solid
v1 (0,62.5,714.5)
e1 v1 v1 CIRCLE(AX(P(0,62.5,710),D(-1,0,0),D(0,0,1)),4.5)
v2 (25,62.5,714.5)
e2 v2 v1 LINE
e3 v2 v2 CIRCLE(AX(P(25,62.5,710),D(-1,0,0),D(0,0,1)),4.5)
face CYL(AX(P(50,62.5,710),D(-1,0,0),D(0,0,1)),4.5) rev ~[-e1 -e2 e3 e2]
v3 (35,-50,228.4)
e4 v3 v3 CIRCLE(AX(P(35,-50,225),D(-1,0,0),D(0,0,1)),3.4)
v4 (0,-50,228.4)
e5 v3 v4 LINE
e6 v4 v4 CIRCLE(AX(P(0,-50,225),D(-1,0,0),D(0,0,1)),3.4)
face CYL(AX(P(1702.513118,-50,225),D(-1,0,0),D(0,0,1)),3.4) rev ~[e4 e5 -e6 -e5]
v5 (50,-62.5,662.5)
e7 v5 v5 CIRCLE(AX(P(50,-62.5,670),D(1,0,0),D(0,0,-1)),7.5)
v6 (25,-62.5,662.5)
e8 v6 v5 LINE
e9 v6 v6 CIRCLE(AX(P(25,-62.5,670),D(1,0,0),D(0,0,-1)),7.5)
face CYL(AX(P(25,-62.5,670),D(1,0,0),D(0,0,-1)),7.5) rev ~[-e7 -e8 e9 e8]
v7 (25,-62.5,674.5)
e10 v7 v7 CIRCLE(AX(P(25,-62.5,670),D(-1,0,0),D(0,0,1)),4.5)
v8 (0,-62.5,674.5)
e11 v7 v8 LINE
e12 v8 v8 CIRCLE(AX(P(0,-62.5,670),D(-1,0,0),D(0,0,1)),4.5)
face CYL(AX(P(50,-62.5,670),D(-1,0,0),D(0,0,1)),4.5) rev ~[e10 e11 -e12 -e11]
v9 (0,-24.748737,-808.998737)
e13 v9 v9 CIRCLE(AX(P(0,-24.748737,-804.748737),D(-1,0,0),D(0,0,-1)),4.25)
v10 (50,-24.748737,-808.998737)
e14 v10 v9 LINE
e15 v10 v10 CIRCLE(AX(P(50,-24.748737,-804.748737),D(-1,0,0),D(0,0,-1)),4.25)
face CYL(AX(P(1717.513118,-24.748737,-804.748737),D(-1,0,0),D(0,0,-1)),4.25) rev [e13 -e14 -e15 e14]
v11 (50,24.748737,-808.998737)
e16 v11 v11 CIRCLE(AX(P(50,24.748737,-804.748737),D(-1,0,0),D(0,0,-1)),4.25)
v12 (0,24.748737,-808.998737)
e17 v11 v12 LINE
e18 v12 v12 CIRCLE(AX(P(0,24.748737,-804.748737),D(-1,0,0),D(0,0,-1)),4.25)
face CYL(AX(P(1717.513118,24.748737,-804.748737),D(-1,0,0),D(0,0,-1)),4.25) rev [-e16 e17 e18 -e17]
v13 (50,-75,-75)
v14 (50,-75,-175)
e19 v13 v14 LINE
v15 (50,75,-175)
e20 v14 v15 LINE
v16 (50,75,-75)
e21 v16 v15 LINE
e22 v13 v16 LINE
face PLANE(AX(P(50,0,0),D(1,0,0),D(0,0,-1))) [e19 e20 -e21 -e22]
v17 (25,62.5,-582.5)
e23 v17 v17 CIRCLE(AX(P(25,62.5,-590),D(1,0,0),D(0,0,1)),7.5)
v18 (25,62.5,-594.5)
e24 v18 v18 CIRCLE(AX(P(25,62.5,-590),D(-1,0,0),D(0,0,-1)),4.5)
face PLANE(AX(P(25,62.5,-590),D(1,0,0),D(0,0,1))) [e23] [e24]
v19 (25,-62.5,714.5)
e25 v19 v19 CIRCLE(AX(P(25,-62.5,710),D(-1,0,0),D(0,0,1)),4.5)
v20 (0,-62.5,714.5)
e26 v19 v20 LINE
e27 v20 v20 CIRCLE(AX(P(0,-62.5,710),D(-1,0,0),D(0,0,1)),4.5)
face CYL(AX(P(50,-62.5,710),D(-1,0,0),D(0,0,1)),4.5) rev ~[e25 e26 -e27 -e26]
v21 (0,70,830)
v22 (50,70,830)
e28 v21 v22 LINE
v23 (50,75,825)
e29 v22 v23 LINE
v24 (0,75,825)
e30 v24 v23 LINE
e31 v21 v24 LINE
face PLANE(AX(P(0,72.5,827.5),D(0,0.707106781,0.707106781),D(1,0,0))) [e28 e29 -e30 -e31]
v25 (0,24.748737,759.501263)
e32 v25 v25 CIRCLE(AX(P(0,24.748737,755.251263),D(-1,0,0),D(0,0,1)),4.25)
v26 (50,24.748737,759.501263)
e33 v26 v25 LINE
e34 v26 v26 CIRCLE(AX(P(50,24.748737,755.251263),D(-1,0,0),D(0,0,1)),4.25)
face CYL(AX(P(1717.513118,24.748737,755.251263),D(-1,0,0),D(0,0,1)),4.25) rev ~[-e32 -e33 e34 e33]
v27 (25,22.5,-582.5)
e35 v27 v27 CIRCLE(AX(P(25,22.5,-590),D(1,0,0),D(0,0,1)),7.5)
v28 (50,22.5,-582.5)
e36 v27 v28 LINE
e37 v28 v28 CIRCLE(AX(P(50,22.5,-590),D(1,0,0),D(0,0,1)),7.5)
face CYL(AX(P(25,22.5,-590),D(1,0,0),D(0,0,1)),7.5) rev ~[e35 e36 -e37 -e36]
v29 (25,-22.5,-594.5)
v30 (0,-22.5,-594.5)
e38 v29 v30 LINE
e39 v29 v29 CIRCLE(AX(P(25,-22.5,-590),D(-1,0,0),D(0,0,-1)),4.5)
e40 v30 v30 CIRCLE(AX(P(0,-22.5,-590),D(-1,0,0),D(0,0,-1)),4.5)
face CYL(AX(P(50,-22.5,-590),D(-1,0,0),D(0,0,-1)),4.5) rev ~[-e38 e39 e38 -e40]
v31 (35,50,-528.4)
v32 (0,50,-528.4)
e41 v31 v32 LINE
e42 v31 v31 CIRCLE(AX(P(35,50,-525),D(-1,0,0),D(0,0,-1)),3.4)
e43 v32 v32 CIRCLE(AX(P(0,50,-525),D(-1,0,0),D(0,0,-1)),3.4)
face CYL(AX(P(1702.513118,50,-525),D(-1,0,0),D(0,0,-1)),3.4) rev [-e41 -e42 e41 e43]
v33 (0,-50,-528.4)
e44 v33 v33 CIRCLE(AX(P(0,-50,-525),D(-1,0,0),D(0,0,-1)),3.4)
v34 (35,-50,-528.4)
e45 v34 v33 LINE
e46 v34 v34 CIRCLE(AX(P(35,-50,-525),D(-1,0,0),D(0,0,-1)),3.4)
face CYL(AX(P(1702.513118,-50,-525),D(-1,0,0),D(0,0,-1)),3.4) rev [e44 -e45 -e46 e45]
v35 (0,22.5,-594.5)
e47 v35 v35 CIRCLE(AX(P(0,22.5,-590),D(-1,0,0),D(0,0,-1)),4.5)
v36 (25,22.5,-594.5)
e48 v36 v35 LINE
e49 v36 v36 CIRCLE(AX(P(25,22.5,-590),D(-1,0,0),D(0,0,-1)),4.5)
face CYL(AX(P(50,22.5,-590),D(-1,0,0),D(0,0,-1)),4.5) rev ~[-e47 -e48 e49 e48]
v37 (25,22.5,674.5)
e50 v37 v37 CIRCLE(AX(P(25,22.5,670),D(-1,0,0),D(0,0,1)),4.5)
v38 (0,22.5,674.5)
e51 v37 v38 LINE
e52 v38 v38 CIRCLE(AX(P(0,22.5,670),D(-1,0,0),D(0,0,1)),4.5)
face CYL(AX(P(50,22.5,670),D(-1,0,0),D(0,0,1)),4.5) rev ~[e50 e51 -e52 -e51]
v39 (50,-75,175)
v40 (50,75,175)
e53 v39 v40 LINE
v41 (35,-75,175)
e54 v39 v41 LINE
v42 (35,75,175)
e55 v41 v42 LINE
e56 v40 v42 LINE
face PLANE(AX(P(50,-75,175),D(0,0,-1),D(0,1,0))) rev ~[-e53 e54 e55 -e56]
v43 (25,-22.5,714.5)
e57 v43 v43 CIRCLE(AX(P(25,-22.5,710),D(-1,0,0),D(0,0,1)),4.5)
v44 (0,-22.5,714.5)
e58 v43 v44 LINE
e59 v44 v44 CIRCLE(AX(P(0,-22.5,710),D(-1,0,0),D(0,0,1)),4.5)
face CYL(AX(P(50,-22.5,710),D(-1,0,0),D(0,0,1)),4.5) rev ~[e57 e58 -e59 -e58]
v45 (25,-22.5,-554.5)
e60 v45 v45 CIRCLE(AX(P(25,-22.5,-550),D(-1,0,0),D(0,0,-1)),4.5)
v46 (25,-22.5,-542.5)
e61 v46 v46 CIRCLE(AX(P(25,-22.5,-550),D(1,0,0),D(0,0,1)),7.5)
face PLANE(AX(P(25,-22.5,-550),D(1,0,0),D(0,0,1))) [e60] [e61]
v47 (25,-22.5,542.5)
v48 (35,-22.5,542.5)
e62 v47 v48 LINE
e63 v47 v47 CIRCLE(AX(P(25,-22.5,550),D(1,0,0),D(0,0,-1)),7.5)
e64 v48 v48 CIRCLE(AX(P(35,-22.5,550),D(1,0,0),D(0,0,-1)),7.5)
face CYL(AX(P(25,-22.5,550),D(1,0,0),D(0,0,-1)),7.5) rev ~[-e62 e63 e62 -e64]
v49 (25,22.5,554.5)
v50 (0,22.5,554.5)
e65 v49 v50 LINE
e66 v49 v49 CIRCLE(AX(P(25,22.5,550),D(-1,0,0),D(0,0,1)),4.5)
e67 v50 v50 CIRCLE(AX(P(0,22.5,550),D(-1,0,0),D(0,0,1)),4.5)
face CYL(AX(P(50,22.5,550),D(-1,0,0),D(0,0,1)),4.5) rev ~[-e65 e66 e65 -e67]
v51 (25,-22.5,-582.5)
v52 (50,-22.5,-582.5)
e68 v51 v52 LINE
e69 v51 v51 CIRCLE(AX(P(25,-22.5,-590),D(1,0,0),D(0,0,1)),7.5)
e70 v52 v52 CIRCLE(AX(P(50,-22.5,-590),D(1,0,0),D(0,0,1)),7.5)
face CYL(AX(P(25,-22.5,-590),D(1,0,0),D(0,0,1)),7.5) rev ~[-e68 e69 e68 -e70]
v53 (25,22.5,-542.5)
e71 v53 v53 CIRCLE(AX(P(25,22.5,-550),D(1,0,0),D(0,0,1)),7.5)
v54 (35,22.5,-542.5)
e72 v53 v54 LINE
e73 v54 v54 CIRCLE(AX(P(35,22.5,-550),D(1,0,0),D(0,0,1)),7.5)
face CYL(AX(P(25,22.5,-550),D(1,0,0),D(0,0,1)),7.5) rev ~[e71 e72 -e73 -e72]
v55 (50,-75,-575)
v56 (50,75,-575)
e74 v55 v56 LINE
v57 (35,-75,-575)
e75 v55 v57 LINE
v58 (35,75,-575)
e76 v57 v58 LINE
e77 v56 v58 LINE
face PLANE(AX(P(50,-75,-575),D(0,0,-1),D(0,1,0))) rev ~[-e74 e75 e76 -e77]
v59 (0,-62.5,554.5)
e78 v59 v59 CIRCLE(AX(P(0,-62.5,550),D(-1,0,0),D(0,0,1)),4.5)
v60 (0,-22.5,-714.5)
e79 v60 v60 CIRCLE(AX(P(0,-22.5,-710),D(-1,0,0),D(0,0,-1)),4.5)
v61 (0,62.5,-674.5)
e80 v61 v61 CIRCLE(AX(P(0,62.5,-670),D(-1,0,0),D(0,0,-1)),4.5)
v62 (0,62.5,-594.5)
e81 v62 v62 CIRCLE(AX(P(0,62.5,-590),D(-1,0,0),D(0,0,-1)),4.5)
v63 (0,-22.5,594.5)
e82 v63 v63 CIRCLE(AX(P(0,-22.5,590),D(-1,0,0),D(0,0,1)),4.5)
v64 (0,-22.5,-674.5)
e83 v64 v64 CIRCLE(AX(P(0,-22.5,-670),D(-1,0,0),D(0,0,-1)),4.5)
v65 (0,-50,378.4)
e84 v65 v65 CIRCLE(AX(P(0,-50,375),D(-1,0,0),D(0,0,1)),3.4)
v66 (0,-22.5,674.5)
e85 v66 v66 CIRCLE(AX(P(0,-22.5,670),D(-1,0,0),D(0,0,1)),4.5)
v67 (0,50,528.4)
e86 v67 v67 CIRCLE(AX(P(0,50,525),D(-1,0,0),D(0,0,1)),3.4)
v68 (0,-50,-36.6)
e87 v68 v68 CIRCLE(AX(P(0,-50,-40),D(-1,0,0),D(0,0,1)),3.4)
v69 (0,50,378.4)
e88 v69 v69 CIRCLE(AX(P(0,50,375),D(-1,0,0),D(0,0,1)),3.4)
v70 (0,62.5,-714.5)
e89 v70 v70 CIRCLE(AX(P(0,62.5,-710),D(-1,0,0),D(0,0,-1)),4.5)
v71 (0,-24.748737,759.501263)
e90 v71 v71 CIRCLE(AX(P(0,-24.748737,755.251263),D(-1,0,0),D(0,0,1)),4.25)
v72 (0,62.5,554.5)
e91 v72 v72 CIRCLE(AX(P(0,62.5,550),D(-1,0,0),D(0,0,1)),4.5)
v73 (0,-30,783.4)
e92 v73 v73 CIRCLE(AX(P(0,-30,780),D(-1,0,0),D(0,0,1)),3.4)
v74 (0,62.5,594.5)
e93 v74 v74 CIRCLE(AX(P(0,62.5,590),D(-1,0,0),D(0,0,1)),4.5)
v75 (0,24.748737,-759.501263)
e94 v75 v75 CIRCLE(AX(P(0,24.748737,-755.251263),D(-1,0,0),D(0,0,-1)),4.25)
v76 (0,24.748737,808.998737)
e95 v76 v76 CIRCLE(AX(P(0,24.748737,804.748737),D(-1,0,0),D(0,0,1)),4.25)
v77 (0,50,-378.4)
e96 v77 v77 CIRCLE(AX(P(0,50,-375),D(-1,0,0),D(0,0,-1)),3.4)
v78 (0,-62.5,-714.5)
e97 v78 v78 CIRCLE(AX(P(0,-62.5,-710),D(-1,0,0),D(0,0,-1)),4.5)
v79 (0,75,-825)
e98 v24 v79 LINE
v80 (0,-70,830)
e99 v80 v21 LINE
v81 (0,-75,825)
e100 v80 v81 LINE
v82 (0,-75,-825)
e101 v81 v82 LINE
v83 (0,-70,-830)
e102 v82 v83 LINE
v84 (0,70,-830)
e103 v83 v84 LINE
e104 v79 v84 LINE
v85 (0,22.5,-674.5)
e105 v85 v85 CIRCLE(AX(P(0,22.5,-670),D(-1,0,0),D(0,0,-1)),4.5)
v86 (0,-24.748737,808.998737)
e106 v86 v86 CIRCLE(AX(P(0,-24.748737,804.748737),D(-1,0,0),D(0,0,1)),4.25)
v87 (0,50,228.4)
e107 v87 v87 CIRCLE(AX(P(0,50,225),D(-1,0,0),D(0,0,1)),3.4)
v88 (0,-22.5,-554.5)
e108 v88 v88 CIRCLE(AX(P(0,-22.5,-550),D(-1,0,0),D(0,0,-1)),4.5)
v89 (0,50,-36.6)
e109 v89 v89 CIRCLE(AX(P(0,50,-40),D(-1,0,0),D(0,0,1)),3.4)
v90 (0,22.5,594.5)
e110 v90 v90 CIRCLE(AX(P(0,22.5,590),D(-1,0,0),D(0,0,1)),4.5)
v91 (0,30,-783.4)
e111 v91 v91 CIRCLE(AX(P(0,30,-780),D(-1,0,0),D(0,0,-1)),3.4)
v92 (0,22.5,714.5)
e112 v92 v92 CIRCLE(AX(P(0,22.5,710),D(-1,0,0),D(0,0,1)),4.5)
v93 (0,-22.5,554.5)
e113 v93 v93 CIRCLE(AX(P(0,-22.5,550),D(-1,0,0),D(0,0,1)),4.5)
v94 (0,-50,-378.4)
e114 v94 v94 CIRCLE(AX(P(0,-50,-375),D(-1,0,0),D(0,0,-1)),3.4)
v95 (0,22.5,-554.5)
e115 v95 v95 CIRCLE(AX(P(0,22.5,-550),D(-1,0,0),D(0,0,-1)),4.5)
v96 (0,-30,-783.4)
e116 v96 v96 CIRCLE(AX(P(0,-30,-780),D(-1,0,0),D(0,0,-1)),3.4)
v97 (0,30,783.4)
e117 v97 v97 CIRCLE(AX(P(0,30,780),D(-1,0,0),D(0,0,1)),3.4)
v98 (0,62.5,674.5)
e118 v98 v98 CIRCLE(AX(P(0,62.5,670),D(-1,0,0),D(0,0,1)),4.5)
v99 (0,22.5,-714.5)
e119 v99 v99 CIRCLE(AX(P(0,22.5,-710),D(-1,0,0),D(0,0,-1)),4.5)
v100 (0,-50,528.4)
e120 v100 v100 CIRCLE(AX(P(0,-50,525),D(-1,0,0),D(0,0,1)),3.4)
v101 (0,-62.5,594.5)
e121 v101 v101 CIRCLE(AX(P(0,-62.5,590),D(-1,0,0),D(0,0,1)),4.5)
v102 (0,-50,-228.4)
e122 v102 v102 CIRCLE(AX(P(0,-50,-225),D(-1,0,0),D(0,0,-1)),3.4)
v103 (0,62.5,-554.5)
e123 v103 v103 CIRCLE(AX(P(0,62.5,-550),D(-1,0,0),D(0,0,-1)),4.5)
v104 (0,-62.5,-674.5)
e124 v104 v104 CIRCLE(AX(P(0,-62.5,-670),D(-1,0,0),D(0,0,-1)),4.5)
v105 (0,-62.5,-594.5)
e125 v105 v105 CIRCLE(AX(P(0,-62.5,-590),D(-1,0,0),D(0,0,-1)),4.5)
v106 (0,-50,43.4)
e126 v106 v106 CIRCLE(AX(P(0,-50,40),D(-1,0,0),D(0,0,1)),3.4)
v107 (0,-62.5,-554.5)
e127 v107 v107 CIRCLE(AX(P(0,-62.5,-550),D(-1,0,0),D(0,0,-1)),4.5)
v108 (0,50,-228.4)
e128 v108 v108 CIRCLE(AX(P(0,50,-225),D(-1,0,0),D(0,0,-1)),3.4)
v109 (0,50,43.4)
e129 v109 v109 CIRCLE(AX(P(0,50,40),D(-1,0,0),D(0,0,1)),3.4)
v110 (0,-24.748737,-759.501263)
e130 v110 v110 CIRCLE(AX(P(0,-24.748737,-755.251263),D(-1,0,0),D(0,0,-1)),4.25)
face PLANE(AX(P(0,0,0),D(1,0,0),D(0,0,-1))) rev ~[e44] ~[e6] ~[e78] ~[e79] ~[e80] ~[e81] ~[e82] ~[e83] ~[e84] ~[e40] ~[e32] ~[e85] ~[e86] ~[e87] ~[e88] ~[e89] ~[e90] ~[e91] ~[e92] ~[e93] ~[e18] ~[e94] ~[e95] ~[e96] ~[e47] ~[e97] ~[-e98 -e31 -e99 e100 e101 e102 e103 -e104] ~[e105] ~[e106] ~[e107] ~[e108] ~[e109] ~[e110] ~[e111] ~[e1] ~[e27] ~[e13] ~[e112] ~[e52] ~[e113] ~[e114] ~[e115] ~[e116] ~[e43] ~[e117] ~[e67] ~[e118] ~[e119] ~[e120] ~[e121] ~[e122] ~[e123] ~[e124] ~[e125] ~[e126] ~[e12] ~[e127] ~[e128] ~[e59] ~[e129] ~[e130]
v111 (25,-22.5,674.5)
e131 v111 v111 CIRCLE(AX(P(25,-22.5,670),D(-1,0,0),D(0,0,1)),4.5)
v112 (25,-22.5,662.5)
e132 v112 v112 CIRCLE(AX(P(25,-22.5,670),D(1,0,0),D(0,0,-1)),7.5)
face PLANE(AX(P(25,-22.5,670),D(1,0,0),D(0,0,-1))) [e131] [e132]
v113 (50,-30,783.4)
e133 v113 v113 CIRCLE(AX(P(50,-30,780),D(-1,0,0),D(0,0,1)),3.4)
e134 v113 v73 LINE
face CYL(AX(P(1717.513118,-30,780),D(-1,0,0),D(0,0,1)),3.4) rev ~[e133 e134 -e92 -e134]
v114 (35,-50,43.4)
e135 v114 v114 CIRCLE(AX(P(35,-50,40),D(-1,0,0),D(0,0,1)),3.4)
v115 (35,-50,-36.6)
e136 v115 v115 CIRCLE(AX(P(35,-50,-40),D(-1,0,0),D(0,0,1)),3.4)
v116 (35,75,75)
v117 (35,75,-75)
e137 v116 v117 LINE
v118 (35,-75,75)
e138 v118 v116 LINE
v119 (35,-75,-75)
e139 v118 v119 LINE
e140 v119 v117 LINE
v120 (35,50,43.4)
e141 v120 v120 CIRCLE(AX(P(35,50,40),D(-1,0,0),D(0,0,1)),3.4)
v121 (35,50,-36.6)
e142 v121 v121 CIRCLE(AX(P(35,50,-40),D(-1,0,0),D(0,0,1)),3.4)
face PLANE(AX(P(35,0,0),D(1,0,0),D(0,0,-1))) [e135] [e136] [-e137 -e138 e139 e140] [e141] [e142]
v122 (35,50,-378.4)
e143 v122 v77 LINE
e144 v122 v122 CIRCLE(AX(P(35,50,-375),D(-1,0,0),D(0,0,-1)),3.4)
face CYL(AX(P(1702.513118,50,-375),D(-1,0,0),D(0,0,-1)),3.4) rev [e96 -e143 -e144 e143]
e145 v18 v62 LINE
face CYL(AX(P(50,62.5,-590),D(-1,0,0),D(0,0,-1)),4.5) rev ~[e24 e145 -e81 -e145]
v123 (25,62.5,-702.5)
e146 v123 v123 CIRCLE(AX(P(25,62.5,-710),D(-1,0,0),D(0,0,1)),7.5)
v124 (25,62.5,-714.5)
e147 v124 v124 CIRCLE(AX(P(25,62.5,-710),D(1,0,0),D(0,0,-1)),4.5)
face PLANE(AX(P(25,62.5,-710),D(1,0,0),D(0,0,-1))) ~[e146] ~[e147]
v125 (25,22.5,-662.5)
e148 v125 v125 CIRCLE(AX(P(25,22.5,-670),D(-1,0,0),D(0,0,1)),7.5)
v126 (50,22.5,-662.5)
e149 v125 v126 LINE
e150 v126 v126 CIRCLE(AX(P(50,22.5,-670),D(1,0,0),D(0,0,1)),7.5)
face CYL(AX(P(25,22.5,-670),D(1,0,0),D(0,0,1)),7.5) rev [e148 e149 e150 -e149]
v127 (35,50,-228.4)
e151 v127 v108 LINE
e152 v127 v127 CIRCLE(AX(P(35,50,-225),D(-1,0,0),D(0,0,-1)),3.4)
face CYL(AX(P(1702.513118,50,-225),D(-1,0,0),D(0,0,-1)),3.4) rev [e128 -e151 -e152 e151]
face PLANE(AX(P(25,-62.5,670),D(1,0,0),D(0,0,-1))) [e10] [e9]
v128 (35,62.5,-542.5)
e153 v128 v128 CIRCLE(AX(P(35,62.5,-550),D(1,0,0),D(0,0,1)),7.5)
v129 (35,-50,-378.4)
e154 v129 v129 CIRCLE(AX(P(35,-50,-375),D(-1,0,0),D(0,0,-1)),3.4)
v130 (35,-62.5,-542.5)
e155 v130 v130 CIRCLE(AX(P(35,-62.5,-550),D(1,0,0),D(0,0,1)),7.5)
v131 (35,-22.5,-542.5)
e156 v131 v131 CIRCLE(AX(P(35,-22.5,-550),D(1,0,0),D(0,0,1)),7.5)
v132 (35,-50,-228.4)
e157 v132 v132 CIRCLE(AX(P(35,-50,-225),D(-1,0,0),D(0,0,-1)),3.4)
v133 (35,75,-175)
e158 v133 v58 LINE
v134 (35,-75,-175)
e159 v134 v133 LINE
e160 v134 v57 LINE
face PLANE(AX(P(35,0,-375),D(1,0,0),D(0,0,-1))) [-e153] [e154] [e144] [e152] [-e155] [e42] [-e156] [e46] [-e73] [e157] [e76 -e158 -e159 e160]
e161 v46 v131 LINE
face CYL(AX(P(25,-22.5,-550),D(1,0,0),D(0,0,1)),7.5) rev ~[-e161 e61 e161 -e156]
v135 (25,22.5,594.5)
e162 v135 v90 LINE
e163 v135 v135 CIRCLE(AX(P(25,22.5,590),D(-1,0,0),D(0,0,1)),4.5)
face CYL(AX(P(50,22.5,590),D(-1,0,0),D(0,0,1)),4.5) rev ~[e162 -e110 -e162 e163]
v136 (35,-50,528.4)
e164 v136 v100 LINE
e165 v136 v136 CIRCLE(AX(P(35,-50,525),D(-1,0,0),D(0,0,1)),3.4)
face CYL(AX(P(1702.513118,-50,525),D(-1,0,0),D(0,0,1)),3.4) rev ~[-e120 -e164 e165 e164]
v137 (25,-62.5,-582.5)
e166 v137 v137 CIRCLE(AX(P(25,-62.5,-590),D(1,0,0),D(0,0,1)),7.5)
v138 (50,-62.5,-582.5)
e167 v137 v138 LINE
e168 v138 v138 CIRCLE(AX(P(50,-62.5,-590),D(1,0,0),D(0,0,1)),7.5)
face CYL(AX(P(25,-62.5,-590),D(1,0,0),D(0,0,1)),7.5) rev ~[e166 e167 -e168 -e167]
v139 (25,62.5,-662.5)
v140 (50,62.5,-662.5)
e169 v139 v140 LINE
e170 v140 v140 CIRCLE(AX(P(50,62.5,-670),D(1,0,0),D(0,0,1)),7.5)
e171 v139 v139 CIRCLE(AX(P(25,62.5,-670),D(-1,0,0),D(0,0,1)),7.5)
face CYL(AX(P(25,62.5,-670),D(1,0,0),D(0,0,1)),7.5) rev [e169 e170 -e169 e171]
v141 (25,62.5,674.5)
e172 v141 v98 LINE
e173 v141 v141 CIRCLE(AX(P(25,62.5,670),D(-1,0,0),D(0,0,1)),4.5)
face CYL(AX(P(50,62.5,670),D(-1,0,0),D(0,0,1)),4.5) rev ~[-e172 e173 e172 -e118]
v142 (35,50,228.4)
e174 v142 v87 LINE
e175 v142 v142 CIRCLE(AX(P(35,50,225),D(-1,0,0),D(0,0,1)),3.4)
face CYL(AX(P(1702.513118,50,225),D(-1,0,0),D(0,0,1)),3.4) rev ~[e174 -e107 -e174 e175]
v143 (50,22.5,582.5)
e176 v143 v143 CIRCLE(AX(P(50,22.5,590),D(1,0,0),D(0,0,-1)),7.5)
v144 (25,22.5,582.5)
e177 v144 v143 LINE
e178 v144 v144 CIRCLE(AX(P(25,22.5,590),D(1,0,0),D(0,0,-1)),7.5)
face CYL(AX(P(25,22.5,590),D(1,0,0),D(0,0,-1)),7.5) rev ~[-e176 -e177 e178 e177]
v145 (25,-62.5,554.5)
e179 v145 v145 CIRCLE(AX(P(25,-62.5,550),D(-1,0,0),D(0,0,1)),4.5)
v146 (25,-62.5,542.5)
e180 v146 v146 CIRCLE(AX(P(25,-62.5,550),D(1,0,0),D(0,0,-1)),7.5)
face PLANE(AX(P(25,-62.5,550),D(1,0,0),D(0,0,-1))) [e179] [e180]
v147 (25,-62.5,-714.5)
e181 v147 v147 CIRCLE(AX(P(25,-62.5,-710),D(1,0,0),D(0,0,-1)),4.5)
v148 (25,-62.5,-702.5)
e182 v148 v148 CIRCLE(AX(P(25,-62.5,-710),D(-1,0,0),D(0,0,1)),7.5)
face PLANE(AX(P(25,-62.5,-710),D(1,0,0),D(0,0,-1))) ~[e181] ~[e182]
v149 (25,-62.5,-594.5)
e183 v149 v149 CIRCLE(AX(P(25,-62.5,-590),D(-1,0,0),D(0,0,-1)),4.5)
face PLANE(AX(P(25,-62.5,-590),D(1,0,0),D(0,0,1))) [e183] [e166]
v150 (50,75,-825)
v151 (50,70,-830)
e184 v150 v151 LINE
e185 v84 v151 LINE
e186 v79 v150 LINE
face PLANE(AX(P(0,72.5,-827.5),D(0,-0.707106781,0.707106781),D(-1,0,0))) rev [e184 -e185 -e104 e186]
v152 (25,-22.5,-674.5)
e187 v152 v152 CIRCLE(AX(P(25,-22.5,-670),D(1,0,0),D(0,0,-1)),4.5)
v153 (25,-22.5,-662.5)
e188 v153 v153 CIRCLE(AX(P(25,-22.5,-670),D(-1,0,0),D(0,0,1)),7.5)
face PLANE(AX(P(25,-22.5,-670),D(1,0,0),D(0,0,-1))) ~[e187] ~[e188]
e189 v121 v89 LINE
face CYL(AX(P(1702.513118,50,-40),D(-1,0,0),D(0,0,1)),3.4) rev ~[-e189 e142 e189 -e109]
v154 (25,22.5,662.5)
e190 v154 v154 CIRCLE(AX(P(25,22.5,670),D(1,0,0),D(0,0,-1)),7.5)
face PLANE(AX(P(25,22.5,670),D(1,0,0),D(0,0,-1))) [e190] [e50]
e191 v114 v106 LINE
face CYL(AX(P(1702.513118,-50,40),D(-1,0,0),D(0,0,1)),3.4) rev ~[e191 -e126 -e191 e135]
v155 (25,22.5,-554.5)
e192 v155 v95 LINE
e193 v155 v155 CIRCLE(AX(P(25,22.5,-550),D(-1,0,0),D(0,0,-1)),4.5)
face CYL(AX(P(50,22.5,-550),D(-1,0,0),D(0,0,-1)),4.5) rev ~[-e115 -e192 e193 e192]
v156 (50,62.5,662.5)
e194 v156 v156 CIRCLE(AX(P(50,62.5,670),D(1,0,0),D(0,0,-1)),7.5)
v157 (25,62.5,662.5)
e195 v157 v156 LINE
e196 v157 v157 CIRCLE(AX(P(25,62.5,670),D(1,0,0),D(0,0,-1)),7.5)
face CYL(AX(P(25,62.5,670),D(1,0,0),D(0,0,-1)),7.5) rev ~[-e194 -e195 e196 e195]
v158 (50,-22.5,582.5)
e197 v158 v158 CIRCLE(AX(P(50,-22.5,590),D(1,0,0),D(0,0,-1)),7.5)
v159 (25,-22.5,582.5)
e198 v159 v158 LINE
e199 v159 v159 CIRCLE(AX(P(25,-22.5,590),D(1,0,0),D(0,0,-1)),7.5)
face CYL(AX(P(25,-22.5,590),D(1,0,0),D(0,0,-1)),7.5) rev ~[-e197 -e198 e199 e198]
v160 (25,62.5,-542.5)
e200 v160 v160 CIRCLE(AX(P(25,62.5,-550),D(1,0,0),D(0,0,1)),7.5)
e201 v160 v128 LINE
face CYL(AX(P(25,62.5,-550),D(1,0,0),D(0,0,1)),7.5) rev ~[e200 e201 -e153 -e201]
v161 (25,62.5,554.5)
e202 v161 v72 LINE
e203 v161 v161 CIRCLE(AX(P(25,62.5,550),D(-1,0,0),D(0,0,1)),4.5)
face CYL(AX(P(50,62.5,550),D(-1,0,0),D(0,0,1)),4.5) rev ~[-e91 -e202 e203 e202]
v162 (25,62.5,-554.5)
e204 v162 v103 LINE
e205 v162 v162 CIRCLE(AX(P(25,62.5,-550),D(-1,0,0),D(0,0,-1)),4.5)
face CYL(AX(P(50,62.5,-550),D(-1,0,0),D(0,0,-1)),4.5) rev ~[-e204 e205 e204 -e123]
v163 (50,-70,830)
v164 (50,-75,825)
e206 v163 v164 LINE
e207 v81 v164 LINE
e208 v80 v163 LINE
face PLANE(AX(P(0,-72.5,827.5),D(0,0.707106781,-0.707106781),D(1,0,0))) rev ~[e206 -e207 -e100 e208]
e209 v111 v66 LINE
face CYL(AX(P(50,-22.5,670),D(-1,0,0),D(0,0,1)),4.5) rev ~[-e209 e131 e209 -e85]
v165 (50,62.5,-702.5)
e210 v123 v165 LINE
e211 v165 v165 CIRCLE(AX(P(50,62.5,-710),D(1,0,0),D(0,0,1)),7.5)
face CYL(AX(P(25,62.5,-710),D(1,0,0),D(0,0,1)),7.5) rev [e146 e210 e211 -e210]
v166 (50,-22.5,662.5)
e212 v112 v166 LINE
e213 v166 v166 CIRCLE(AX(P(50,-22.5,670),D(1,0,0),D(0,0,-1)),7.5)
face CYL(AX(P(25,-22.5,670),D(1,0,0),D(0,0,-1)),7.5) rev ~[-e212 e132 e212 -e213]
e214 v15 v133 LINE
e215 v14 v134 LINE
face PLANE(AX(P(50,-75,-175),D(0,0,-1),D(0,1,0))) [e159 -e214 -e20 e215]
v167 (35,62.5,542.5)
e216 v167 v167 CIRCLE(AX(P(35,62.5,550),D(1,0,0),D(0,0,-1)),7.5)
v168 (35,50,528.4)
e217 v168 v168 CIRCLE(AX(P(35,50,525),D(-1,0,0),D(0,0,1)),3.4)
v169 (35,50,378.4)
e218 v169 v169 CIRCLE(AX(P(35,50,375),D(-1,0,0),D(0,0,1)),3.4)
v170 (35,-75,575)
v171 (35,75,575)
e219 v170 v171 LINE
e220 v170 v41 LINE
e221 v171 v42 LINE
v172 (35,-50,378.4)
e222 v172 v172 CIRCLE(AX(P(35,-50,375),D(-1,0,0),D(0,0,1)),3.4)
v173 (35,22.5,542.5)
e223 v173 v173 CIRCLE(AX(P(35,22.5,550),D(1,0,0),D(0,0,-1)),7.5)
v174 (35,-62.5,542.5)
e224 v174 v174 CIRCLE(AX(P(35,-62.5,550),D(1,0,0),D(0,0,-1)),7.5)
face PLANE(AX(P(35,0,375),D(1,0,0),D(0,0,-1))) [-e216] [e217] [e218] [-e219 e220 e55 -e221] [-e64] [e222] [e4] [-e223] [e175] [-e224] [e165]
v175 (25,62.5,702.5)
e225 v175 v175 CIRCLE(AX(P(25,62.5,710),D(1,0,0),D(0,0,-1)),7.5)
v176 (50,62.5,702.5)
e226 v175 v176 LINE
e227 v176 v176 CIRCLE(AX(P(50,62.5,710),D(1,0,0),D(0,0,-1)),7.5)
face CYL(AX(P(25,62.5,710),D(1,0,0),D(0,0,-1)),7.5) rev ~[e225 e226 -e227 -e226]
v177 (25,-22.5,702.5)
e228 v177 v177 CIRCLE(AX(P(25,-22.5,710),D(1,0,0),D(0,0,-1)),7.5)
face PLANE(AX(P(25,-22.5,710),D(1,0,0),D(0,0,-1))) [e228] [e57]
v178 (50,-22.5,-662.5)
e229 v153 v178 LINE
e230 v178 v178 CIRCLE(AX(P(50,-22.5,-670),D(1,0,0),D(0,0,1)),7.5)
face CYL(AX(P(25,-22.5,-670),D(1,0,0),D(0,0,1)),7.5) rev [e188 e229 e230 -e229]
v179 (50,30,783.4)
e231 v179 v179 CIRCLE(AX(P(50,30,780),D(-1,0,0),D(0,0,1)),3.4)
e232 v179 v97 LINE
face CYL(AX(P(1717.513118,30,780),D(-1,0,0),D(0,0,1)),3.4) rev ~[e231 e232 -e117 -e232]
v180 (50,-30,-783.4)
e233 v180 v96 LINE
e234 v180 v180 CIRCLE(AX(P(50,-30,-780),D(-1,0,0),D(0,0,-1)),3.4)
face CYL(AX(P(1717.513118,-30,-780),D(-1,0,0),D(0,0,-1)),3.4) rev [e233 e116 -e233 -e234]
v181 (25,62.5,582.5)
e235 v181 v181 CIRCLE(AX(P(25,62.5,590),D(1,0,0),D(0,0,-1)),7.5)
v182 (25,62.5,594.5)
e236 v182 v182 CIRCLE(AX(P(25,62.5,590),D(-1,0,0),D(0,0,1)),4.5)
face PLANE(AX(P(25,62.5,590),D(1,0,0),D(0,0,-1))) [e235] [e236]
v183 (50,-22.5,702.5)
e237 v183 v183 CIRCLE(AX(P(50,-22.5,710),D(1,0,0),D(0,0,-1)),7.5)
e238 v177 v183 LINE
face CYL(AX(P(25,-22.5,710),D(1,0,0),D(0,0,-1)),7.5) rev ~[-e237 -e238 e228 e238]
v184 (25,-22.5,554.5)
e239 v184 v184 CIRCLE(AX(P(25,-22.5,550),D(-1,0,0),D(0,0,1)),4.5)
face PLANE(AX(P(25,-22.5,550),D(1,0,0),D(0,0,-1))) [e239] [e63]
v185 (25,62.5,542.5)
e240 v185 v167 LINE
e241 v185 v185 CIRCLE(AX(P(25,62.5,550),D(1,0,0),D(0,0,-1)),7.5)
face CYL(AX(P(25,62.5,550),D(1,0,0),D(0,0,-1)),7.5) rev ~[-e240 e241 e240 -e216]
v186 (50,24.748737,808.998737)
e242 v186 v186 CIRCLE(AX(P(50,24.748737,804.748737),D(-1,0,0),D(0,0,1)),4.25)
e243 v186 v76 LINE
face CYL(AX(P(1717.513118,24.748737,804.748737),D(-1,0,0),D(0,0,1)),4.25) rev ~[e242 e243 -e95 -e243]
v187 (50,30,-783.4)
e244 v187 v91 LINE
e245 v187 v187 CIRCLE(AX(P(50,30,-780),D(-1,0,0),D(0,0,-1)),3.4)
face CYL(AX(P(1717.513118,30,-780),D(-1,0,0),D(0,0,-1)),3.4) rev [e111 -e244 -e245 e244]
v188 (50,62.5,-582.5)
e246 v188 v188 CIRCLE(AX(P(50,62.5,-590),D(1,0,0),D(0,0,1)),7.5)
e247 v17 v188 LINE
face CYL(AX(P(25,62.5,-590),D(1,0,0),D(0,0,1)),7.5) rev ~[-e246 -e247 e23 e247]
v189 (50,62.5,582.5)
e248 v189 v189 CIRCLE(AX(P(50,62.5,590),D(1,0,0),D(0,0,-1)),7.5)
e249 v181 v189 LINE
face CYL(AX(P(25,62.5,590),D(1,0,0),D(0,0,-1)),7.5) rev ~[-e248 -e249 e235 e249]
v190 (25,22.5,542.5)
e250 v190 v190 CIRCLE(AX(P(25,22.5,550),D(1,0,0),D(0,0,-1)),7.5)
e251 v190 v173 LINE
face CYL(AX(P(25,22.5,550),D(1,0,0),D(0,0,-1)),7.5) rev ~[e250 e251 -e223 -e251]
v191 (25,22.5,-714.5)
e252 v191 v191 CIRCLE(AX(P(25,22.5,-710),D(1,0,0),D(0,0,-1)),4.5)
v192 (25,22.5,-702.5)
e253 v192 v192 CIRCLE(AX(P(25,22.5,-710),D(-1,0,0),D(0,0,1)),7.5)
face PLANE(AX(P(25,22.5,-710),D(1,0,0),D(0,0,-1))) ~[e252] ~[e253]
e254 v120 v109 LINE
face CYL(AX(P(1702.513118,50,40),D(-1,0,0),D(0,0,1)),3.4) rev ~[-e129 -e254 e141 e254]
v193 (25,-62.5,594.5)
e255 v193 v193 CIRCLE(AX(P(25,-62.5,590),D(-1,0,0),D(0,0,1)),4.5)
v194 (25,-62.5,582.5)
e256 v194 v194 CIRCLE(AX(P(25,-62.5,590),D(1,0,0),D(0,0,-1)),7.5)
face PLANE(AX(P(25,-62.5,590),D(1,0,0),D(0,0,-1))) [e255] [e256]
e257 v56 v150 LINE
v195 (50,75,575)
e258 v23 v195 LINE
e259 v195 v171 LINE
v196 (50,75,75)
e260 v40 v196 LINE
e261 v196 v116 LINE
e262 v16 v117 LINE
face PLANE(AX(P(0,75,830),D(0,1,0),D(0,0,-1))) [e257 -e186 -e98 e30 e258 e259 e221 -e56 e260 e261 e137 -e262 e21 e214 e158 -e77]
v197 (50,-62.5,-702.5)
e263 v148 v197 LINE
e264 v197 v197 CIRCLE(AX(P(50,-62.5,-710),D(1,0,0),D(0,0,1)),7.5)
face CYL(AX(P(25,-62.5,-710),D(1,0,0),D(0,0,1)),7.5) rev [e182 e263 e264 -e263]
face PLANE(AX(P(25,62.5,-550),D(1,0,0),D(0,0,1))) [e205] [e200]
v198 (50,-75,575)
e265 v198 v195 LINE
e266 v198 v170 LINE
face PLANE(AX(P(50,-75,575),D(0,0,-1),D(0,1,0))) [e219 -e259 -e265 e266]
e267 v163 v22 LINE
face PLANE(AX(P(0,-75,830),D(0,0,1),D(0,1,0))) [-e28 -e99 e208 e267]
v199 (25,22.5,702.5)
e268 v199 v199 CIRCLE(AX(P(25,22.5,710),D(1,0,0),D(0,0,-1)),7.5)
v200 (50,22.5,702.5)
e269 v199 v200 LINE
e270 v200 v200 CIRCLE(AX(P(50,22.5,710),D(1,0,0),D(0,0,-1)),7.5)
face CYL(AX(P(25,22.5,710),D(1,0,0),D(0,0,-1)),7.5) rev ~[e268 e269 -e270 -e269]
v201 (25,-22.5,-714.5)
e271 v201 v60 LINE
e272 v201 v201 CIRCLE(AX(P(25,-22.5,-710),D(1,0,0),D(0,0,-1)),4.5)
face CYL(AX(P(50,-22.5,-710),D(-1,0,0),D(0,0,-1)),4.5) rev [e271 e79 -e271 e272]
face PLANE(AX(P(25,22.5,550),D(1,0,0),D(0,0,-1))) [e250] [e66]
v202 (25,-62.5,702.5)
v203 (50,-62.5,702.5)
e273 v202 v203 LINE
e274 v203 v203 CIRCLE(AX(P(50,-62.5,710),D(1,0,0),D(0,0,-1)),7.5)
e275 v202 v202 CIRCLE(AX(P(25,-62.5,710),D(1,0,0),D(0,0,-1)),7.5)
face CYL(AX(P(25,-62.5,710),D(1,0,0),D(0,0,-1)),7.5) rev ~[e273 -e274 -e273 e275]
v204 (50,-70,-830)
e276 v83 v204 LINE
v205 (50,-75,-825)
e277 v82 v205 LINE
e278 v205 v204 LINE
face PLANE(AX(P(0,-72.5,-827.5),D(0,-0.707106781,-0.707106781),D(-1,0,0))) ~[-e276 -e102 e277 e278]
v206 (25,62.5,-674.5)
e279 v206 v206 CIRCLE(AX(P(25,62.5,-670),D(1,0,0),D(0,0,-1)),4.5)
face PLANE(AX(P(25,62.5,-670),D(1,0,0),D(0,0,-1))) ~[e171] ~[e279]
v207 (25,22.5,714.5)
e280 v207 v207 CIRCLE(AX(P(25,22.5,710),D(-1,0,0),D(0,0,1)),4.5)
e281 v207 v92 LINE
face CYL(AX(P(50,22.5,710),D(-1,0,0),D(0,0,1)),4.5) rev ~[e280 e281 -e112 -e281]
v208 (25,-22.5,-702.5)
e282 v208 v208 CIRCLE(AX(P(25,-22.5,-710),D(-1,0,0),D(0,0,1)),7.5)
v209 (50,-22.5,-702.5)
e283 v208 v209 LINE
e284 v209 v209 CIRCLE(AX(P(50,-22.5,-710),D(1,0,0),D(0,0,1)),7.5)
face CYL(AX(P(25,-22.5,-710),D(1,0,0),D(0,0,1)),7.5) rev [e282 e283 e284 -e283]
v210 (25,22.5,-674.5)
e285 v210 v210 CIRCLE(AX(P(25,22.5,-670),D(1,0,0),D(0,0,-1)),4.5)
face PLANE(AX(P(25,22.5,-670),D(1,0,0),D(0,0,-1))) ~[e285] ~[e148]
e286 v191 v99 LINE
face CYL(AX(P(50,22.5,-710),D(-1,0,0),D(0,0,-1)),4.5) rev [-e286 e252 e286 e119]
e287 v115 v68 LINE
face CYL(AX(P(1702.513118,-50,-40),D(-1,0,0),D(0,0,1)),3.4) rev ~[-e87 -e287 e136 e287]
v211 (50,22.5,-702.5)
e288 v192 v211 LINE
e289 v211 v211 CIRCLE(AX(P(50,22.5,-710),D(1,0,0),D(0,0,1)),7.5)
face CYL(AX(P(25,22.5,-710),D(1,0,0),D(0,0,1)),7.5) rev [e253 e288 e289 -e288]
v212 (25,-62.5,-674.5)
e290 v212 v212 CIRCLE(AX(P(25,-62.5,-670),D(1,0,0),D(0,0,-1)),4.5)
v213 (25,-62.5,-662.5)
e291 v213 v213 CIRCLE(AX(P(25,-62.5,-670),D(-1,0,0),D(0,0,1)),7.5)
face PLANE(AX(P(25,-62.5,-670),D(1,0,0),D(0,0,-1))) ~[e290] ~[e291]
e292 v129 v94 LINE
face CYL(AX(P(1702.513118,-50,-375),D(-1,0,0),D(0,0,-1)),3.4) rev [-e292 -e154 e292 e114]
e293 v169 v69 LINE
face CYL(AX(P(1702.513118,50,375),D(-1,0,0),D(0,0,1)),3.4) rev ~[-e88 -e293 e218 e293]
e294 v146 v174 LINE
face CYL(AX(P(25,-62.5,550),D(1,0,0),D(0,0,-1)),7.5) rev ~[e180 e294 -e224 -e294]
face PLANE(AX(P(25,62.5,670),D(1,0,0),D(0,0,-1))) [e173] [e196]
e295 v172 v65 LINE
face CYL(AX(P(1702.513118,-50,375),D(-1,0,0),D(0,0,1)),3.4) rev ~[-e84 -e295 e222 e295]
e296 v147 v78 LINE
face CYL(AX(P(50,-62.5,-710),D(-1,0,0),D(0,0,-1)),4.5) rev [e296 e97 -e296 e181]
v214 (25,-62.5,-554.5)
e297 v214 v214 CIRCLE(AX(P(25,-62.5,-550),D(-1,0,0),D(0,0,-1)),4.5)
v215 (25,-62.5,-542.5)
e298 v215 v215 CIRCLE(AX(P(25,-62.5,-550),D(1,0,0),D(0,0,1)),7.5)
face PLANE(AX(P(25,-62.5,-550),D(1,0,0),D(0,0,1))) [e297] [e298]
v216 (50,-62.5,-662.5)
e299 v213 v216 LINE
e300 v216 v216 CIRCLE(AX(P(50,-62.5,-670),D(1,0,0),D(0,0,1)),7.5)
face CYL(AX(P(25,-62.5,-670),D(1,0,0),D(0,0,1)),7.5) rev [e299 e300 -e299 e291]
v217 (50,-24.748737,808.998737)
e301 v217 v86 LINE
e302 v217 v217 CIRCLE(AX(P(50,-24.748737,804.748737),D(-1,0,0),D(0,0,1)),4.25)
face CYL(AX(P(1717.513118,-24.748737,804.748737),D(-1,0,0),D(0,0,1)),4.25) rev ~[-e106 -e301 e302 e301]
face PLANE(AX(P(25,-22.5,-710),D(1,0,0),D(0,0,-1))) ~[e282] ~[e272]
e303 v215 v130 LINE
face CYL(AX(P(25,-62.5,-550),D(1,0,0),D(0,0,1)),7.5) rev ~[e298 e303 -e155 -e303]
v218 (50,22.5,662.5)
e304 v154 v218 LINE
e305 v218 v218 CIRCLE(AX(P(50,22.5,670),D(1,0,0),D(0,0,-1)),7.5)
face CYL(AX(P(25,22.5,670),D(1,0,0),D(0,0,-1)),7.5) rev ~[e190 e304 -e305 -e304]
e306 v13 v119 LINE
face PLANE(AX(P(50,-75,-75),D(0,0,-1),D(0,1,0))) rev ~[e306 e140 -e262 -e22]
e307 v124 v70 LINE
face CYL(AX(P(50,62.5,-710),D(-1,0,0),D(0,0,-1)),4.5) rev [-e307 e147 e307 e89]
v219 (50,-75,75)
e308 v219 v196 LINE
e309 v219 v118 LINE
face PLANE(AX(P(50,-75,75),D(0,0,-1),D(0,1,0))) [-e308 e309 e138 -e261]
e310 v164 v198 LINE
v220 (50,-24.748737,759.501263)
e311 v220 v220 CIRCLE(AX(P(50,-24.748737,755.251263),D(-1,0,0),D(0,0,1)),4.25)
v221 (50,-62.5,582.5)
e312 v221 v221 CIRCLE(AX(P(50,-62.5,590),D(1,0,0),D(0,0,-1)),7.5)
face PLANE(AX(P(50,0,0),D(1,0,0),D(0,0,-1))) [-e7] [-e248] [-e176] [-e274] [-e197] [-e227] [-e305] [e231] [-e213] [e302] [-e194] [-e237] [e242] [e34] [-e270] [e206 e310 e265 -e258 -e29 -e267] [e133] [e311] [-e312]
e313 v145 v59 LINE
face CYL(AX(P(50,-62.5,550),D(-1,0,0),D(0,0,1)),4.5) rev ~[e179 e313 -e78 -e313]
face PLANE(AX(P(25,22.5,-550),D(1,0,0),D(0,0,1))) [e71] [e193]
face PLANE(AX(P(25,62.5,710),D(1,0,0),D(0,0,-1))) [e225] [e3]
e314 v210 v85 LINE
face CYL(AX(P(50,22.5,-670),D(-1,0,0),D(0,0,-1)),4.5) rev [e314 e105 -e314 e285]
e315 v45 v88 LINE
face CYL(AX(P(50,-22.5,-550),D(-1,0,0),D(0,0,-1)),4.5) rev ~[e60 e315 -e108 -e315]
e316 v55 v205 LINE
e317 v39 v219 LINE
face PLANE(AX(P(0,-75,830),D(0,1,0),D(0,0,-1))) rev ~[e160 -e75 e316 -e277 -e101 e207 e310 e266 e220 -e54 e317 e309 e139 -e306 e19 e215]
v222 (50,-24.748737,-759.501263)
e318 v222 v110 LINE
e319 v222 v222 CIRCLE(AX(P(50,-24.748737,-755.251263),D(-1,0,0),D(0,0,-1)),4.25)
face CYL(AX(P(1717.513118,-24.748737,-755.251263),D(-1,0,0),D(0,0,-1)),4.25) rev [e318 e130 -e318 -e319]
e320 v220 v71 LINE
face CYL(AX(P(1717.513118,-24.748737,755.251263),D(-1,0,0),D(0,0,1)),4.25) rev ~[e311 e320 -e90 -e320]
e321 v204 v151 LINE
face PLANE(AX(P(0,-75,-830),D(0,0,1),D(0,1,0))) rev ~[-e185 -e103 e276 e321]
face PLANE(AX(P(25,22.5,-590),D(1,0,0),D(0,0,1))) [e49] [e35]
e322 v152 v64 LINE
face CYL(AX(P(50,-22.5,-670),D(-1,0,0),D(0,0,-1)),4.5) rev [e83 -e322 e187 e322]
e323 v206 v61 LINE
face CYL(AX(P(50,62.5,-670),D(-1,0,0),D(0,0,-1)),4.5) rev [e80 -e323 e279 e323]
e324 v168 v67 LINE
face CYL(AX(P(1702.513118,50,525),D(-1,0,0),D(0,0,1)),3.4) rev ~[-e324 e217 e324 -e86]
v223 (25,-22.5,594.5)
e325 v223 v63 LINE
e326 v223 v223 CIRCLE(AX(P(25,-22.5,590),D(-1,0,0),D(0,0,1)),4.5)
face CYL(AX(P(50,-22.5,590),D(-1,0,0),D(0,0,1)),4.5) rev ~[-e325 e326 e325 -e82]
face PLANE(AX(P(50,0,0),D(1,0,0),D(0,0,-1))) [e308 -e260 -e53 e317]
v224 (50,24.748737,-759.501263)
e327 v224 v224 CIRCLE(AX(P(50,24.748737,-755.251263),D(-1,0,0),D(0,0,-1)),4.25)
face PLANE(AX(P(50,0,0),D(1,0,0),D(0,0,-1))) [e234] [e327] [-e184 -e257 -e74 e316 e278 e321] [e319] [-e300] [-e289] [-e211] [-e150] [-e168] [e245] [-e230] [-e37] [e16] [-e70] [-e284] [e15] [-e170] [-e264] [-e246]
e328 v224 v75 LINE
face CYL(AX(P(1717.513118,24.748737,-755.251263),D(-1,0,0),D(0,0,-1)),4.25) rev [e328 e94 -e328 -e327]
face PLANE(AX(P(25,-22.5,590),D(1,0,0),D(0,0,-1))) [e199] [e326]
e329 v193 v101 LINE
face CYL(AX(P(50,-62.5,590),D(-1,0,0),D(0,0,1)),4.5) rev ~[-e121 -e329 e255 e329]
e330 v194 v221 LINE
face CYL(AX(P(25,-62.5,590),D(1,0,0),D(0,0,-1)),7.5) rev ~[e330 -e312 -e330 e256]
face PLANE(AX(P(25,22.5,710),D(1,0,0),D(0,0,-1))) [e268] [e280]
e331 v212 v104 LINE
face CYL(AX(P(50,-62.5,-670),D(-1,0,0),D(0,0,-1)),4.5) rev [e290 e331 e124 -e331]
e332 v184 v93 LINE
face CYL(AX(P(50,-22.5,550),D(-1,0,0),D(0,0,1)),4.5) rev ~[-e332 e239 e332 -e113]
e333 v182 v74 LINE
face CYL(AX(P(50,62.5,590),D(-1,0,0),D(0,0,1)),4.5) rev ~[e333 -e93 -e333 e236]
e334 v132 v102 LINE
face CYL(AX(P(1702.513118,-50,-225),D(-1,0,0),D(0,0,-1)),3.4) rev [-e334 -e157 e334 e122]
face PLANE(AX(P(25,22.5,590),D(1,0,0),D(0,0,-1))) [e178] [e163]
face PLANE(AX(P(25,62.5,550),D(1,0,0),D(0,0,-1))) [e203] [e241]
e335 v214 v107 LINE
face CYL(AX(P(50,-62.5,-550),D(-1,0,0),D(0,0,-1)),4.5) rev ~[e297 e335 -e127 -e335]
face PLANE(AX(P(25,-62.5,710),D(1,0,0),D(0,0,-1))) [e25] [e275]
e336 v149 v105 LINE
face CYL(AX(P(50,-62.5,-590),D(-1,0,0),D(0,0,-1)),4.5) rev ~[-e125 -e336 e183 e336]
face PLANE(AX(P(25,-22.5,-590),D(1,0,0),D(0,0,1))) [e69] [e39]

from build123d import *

# Parameters (mm, degrees)
SKETCH_1_W                  = 1660
SKETCH_1_H                  = 150
EXTRUDE_1_DEPTH             = 50
HOLE_WIZARD_M10_1_D         = 8.5
SKETCH_4_W                  = 150
SKETCH_4_H                  = 150
SKETCH_4_W_2                = 400
CUT_EXTRUDE_1_DEPTH         = 15
HOLE_WIZARD_M8_1_D          = 6.8
HOLE_WIZARD_M8_2_D          = 6.8
HOLE_WIZARD_1_D             = 9
HOLE_WIZARD_1_CBORE_D       = 15
HOLE_WIZARD_1_CBORE_DEPTH   = 25
PATTERN_LINEAR_1_COUNT      = 2
PATTERN_LINEAR_1_PITCH      = 120
MIRROR_3_COPY_1_D           = 9
MIRROR_3_COPY_1_CBORE_D     = 15
MIRROR_3_COPY_1_CBORE_DEPTH = 25
HOLE_WIZARD_M8_3_D          = 6.8
CHAMFER_1_SIZE              = 5


with BuildPart() as part:
    # 草图1 → 凸台-拉伸1 (new body)
    with BuildSketch(Plane(origin=(0, 0, 0), x_dir=(0, 0, -1), z_dir=(1, 0, 0))):
        Rectangle(SKETCH_1_W, SKETCH_1_H)
    extrude(amount=EXTRUDE_1_DEPTH)

    # M10 螺纹孔1 (through all)
    with Locations(Plane(origin=(50, 0, 0), x_dir=(0, 0, -1), z_dir=(1, 0, 0))):
        with Locations((-804.748737342, 24.748737342), (-755.251262658, 24.748737342), (-804.748737342, -24.748737342), (-755.251262658, -24.748737342)):
            hole_wizard_m10_1 = Hole(HOLE_WIZARD_M10_1_D / 2)

    # 镜向1: M10 螺纹孔1 across plane
    add(hole_wizard_m10_1.mirror(Plane.XY), mode=Mode.SUBTRACT)

    # 草图4 → 切除-拉伸1 (cut)
    with BuildSketch(Plane(origin=(50, 0, 0), x_dir=(0, 0, -1), z_dir=(1, 0, 0))):
        Rectangle(SKETCH_4_W, SKETCH_4_H)
        with Locations((-375, 0)):
            Rectangle(SKETCH_4_W_2, SKETCH_4_H)
        with Locations((375, 0)):
            Rectangle(SKETCH_4_W_2, SKETCH_4_H)
    extrude(amount=-CUT_EXTRUDE_1_DEPTH, mode=Mode.SUBTRACT)

    # M8 螺纹孔1 (through all)
    with Locations(Plane(origin=(35, 0, 0), x_dir=(0, 0, -1), z_dir=(1, 0, 0))):
        with Locations((-525, 50), (-375, 50), (-225, 50), (-525, -50), (-375, -50), (-225, -50)):
            hole_wizard_m8_1 = Hole(HOLE_WIZARD_M8_1_D / 2)

    # 镜向2: M8 螺纹孔1 across plane
    add(hole_wizard_m8_1.mirror(Plane.XY), mode=Mode.SUBTRACT)

    # M8 螺纹孔2 (through all)
    with Locations(Plane(origin=(35, 0, 0), x_dir=(0, 0, -1), z_dir=(1, 0, 0))):
        with Locations((-40, 50), (40, 50), (-40, -50), (40, -50)):
            Hole(HOLE_WIZARD_M8_2_D / 2)

    # 打孔尺寸(%根据)内六角圆柱头螺钉的类型1 (through all)
    with Locations(Plane(origin=(50, 0, 0), x_dir=(0, 0, -1), z_dir=(1, 0, 0))):
        with Locations((-710, -22.5), (-710, -62.5), (-670, -22.5), (-670, -62.5), (-670, 62.5), (-670, 22.5), (-710, 62.5), (-710, 22.5)):
            hole_wizard_1 = CounterBoreHole(HOLE_WIZARD_1_D / 2, HOLE_WIZARD_1_CBORE_D / 2, HOLE_WIZARD_1_CBORE_DEPTH)

    # 阵列(线性)1: 打孔尺寸(%根据)内六角圆柱头螺钉的类型1 ×2
    with Locations(*[(0, 0, -i * PATTERN_LINEAR_1_PITCH) for i in range(1, PATTERN_LINEAR_1_COUNT)]):
        add(hole_wizard_1, mode=Mode.SUBTRACT)

    # 镜向3: 打孔尺寸(%根据)内六角圆柱头螺钉的类型1 across plane
    add(hole_wizard_1.mirror(Plane.XY), mode=Mode.SUBTRACT)

    # 镜向3 copy 1 (through all)
    with Locations(Plane(origin=(50, 0, 120), x_dir=(0, 0, 1), z_dir=(1, 0, 0))):
        with Locations((-710, 22.5), (-710, 62.5), (-670, 22.5), (-670, 62.5), (-670, -62.5), (-670, -22.5), (-710, -62.5), (-710, -22.5)):
            CounterBoreHole(MIRROR_3_COPY_1_D / 2, MIRROR_3_COPY_1_CBORE_D / 2, MIRROR_3_COPY_1_CBORE_DEPTH)

    # M8 螺纹孔3 (through all)
    with Locations(Plane(origin=(50, 0, 0), x_dir=(0, 0, -1), z_dir=(1, 0, 0))):
        with Locations((-780, 30), (-780, -30)):
            hole_wizard_m8_3 = Hole(HOLE_WIZARD_M8_3_D / 2)

    # 镜向4: M8 螺纹孔3 across plane
    add(hole_wizard_m8_3.mirror(Plane.XY), mode=Mode.SUBTRACT)

    # 倒角1
    chamfer_1_edges = [part.edges().sort_by_distance(p)[0] for p in [
        (25, -75, -830),
        (25, -75, 830),
        (25, 75, 830),
        (25, 75, -830),
    ]]
    chamfer(chamfer_1_edges, length=CHAMFER_1_SIZE)


solid = part.part
